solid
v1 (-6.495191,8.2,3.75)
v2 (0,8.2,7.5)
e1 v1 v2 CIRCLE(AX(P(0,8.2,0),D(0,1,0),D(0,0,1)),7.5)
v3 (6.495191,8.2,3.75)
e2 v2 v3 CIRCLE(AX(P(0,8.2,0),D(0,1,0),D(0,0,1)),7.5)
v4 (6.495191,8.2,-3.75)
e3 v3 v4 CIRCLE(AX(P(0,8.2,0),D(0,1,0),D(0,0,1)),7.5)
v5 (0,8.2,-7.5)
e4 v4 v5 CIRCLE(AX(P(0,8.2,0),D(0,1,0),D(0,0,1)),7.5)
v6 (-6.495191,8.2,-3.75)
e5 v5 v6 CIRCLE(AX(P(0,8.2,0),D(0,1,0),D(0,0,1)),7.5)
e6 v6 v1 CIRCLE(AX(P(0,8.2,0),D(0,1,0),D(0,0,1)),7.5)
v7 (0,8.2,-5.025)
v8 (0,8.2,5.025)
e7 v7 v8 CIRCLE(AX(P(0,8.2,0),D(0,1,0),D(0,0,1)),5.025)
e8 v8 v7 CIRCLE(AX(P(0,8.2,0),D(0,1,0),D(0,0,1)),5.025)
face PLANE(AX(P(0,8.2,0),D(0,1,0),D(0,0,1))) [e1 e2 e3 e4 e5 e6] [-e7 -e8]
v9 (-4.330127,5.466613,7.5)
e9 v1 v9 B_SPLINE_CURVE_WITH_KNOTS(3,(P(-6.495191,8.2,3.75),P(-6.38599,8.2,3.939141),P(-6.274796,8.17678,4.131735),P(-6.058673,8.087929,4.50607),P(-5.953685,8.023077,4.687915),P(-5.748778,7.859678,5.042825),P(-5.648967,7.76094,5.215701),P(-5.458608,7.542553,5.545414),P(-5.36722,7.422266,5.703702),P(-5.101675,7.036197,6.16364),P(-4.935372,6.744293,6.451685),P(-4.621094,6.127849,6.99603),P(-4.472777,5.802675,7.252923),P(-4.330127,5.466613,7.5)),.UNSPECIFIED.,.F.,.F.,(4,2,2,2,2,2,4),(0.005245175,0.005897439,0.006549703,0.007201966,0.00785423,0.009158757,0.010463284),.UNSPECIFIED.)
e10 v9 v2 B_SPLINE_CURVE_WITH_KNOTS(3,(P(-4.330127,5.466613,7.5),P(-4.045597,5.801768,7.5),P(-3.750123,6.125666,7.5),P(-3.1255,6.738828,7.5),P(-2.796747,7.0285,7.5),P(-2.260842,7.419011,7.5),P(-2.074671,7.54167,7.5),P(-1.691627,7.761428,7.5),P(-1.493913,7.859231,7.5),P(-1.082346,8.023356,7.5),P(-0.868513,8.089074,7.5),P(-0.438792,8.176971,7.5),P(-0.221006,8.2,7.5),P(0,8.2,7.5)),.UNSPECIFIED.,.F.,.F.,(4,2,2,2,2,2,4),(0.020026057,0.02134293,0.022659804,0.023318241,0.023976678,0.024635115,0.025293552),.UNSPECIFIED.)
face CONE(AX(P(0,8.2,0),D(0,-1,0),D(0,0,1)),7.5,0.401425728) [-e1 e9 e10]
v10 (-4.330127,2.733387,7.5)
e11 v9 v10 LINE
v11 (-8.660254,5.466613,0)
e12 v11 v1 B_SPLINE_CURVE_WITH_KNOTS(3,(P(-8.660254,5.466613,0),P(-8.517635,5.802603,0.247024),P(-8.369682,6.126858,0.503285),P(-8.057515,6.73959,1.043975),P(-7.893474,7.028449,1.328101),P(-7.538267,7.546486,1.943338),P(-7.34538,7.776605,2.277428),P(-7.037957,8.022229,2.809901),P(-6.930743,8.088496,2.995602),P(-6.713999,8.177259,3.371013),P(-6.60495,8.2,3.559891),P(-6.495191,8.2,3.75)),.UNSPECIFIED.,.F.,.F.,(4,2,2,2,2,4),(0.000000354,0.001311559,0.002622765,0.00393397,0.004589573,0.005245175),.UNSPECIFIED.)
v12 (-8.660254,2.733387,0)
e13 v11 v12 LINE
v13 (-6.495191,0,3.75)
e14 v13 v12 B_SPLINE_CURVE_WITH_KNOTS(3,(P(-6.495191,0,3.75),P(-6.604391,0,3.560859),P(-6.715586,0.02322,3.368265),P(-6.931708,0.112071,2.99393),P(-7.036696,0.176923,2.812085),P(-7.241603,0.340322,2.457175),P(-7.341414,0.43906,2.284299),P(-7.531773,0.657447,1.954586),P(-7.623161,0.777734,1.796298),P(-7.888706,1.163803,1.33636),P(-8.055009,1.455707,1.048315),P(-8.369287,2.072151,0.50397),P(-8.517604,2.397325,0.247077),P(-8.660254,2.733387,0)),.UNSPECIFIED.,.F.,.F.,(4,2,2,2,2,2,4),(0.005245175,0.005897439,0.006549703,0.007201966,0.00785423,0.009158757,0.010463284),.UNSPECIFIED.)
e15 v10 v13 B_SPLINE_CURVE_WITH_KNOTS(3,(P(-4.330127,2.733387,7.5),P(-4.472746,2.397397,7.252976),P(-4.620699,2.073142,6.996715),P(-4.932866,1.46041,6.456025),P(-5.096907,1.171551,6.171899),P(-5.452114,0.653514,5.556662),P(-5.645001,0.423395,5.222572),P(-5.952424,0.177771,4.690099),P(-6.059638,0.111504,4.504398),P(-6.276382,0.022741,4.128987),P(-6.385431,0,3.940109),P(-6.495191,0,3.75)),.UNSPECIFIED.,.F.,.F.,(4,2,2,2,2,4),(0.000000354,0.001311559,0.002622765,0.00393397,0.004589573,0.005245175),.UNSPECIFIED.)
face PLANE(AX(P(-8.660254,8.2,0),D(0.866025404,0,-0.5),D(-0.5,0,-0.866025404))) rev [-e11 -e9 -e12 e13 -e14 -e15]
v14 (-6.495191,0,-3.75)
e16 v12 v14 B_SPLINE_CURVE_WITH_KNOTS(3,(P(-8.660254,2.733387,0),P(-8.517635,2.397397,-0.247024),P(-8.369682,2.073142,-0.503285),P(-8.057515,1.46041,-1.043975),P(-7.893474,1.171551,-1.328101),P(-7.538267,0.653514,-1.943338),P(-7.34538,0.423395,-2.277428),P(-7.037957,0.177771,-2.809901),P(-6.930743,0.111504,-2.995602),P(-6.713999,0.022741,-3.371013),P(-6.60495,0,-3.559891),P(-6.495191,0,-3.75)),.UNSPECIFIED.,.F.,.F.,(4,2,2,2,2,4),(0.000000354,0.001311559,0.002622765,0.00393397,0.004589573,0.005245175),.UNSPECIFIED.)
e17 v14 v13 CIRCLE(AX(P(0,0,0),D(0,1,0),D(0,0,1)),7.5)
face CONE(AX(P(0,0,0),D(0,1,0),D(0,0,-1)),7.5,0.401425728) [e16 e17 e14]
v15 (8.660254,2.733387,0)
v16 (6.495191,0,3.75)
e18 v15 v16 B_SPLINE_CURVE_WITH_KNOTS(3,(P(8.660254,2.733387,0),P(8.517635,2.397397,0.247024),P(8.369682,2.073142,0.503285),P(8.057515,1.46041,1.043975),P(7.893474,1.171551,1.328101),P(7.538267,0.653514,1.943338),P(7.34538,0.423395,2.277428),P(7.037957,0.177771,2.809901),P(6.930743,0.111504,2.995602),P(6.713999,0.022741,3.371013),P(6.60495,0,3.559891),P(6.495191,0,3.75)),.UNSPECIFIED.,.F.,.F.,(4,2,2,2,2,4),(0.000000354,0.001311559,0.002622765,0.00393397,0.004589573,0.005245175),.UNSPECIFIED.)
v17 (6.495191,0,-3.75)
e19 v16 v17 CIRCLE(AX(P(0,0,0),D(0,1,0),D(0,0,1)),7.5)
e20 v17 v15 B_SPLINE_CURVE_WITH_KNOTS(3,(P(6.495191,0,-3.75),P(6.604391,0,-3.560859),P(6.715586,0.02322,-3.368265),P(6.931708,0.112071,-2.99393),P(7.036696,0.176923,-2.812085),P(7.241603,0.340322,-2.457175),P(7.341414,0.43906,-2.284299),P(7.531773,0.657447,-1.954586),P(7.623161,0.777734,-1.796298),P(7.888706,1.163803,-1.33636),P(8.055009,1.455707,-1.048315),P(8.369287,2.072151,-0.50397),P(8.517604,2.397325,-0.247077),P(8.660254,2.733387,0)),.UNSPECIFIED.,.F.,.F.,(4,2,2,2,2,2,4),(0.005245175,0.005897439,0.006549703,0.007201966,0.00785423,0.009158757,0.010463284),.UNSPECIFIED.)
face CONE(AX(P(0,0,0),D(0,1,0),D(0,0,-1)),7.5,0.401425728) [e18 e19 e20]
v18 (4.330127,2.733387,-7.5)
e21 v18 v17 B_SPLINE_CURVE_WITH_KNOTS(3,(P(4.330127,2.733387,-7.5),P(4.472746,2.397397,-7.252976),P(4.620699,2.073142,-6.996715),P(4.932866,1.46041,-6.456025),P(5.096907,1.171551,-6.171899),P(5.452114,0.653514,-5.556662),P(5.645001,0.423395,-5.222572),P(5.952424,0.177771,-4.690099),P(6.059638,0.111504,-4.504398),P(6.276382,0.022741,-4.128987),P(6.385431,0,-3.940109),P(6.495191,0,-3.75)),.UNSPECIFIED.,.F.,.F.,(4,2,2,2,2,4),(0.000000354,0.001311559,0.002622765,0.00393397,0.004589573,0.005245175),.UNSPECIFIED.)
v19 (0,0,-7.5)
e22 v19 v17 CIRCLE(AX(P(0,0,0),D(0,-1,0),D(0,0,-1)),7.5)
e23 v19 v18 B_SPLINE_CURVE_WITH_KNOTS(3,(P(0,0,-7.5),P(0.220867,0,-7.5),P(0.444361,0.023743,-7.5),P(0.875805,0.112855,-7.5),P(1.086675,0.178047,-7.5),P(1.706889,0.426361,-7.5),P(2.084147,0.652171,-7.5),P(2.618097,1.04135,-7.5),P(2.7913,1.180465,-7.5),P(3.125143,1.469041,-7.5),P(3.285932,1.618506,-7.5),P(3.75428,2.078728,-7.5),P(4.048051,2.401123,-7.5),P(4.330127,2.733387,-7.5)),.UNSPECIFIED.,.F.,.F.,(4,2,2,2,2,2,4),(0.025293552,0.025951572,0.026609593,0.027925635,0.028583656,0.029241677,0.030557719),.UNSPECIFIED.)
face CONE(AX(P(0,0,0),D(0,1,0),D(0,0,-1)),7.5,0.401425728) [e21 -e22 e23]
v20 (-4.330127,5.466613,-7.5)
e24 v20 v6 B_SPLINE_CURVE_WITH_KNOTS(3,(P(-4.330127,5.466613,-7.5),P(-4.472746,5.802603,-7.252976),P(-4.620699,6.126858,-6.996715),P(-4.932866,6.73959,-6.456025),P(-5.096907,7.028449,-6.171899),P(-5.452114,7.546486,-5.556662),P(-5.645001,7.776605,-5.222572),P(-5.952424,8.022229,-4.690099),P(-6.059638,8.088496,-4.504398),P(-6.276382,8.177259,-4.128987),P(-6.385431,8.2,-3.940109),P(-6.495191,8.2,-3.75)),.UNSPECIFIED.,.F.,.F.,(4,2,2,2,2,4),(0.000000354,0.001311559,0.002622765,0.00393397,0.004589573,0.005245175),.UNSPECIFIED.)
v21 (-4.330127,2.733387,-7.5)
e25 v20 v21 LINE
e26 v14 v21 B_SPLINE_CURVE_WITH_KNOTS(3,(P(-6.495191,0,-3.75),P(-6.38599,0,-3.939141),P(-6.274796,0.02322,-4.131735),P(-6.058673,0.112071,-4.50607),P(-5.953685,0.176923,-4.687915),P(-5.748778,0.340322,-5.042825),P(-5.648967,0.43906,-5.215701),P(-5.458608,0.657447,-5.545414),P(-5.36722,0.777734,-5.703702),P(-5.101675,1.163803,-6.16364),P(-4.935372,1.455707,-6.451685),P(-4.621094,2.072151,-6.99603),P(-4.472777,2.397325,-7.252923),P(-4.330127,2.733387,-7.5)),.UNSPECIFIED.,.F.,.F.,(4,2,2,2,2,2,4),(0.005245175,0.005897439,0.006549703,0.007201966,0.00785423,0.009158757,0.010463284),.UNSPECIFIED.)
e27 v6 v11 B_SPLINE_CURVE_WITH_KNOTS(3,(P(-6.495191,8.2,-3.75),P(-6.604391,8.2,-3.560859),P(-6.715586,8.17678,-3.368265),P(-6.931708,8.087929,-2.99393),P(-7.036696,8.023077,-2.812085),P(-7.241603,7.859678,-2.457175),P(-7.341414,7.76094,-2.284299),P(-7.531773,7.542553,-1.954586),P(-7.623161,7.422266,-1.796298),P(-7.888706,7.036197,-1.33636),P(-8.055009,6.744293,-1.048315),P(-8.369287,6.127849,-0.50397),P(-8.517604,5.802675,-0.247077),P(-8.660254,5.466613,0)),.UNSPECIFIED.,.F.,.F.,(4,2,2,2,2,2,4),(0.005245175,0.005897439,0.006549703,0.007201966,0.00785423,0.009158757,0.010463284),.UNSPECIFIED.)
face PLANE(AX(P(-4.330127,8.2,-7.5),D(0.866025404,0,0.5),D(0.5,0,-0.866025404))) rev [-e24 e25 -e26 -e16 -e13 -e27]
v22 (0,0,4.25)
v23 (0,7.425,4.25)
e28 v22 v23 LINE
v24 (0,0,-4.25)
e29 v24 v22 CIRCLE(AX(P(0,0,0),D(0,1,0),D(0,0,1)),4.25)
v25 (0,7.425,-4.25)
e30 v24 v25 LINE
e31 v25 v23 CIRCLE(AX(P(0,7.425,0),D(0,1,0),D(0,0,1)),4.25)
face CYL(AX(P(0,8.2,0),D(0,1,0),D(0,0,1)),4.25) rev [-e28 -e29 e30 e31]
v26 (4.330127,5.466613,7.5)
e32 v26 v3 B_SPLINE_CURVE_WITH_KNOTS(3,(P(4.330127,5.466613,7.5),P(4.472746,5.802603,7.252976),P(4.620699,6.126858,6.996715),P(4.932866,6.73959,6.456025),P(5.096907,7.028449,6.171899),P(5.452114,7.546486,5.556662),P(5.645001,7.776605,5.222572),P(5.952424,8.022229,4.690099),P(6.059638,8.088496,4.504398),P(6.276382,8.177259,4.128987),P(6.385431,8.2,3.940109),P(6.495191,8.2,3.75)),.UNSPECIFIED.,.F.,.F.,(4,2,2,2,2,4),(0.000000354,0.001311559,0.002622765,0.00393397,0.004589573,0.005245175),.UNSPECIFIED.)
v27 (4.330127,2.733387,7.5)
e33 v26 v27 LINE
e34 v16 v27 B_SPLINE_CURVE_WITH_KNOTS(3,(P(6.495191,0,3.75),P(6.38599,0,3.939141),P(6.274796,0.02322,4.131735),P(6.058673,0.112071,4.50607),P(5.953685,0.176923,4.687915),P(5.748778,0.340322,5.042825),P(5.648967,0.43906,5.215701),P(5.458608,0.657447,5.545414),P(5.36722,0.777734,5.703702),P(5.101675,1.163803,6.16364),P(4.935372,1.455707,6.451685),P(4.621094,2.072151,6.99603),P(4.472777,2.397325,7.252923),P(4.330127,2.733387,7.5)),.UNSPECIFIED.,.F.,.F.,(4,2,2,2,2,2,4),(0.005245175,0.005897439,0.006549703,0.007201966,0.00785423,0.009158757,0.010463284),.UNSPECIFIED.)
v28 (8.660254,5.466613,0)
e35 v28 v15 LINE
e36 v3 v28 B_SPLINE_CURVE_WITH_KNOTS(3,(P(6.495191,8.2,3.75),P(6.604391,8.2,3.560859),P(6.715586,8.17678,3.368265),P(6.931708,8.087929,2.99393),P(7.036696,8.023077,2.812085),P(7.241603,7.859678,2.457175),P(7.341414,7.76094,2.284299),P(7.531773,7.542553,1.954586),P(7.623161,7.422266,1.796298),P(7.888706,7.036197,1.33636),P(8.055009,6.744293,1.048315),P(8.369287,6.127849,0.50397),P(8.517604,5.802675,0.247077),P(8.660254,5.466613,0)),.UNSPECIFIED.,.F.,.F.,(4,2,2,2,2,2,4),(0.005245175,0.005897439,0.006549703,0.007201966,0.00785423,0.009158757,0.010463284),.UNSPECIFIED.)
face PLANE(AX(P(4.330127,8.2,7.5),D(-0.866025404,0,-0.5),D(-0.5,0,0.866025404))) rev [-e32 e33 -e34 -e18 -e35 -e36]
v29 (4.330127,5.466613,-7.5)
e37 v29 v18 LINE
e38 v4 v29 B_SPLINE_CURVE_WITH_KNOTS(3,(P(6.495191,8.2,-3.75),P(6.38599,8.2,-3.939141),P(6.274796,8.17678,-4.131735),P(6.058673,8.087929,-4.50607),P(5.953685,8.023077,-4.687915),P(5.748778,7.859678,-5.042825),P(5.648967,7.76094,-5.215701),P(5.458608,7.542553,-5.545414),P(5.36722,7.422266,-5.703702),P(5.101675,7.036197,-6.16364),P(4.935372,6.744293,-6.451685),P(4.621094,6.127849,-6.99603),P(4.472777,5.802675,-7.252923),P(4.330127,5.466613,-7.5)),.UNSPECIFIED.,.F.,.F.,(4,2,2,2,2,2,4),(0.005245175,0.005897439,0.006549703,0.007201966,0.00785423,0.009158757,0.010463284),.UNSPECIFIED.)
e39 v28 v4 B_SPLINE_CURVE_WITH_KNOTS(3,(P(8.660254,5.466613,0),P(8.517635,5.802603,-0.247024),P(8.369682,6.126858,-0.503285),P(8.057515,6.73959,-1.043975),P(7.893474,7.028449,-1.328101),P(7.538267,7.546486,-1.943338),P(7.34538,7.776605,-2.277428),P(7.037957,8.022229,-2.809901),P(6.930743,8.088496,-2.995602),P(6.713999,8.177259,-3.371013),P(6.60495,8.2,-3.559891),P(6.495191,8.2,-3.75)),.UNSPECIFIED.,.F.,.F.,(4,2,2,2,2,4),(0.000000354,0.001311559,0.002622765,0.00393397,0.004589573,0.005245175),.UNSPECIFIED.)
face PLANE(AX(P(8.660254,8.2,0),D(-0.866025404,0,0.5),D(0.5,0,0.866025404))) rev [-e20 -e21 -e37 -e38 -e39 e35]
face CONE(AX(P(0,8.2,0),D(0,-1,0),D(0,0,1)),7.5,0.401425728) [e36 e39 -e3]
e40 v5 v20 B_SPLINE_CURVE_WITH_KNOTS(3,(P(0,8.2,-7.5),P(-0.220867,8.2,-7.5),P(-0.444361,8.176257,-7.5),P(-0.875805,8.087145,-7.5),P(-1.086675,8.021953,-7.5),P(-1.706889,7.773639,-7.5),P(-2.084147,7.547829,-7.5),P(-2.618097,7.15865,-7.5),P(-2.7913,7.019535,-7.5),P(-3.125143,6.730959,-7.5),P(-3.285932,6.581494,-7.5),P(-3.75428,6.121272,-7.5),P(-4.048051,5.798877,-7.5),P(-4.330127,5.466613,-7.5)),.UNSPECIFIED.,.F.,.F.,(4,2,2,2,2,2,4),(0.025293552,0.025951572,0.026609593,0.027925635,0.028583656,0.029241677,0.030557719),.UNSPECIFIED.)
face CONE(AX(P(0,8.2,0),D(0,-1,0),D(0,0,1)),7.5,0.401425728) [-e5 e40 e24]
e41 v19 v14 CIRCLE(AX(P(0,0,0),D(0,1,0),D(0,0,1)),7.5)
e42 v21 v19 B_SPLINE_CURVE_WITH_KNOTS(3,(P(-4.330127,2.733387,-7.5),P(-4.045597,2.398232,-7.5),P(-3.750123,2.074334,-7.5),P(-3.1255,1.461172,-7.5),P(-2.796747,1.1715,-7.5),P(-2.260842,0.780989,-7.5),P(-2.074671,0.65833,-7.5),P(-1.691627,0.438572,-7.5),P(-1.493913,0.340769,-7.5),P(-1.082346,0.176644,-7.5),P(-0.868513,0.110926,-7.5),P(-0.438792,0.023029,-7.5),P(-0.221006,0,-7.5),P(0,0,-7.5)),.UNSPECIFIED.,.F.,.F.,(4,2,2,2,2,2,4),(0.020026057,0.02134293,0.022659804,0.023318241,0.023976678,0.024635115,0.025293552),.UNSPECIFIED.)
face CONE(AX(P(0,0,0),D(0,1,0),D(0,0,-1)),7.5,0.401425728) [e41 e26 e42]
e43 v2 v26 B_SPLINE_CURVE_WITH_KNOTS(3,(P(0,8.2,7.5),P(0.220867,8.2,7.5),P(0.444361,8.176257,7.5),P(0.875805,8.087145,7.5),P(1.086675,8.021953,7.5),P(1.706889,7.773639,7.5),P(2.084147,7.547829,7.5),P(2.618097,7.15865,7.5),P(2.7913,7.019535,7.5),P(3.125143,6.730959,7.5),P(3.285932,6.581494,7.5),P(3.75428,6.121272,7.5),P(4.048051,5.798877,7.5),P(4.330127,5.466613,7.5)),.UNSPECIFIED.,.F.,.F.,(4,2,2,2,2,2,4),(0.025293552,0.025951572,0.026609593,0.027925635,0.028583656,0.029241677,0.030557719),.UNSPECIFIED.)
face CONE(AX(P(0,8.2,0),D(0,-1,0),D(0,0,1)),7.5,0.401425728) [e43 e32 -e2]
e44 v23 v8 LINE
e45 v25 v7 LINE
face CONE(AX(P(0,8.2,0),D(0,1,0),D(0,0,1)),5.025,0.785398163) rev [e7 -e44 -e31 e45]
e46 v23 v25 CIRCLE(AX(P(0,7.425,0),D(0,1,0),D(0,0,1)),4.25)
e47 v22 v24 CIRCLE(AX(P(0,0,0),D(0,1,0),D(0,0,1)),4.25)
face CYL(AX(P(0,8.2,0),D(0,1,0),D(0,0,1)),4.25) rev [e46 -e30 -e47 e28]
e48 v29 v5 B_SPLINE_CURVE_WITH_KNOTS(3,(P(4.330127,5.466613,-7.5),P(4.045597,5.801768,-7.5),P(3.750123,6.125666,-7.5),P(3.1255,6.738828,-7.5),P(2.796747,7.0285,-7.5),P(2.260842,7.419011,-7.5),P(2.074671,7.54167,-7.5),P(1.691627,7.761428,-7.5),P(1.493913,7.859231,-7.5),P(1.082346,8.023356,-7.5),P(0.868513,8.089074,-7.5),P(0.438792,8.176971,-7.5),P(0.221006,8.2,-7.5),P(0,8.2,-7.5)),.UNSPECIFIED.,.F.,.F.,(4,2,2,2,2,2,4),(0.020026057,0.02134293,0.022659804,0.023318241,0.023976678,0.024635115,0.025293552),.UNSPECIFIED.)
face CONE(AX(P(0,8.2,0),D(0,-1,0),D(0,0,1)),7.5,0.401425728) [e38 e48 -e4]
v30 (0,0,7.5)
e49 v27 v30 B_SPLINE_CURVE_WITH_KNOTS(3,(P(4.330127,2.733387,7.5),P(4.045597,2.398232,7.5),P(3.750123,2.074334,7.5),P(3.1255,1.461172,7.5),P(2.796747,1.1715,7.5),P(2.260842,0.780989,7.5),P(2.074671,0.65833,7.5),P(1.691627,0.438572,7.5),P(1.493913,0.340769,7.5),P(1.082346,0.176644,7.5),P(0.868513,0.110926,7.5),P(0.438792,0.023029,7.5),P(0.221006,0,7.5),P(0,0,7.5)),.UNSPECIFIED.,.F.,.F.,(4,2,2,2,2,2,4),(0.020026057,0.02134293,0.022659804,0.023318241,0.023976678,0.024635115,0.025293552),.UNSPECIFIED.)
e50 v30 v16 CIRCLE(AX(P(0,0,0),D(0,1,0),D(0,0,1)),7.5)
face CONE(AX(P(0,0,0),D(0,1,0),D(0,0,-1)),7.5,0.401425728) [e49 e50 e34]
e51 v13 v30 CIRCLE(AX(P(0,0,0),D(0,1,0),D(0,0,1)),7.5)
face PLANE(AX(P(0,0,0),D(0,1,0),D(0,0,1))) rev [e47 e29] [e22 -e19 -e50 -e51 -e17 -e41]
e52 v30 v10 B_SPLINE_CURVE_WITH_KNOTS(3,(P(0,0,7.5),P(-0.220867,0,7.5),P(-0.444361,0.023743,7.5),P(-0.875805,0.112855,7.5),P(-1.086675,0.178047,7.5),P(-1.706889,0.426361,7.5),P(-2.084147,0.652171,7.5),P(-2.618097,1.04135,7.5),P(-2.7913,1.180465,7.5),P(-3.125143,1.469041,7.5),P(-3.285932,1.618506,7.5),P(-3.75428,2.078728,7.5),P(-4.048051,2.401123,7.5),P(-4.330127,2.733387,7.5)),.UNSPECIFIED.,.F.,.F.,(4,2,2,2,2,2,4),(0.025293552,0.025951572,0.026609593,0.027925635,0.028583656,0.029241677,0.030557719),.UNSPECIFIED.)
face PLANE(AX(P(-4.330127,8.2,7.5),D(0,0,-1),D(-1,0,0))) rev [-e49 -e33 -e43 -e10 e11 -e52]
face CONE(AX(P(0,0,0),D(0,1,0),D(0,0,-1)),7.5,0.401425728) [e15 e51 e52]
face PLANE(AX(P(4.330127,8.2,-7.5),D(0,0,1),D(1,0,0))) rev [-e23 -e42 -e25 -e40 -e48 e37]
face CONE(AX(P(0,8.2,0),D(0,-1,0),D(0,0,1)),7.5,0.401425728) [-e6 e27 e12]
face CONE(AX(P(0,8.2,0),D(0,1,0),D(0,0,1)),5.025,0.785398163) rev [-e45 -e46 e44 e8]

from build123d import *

# Parameters (mm, degrees)
BOSS_EXTRUDE1_DEPTH          = 8.2
SKETCH2_OUTSIDE_W            = 31.148
SKETCH2_OUTSIDE_H            = 28.828
SKETCH2_OUTSIDE_R            = 7.5
CUT_EXTRUDE1_DEPTH           = 8.2
CUT_EXTRUDE1_DRAFT           = -23
SKETCH3_OUTSIDE_W            = 31.148
SKETCH3_OUTSIDE_H            = 28.828
SKETCH3_OUTSIDE_R            = 7.5
CUT_EXTRUDE2_DEPTH           = 8.2
CUT_EXTRUDE2_DRAFT           = -23
M10_TAPPED_HOLE1_D           = 8.5
M10_TAPPED_HOLE1_CSINK_D     = 10.05
M10_TAPPED_HOLE1_CSINK_ANGLE = 90


with BuildPart() as part:
    # Sketch1 → Boss-Extrude1 (new body)
    with BuildSketch(Plane(origin=(0, 0, 0), x_dir=(1, 0, 0), z_dir=(0, 1, 0))):
        Polygon((4.330127019, 7.5), (-4.330127019, 7.5), (-8.660254038, 0), (-4.330127019, -7.5), (4.330127019, -7.5), (8.660254038, 0), align=None)
    extrude(amount=BOSS_EXTRUDE1_DEPTH)


with BuildPart() as cut_extrude1_tool:
    # Sketch2 outside → Cut-Extrude1 (with draft: the straight prism first)
    with BuildSketch(Plane(origin=(0, 8.2, 0), x_dir=(1, 0, 0), z_dir=(0, 1, 0))):
        Rectangle(SKETCH2_OUTSIDE_W, SKETCH2_OUTSIDE_H)
        Circle(SKETCH2_OUTSIDE_R, mode=Mode.SUBTRACT)
    extrude(amount=-CUT_EXTRUDE1_DEPTH)
    # Cut-Extrude1: the draft: its side faces are tilted about the plane it starts from
    cut_extrude1_sides = [cut_extrude1_tool.faces().sort_by_distance(p)[0] for p in [
        (0, 4.1, 14.414),
        (15.574, 4.1, 0),
        (0, 4.1, -14.414),
        (-15.574, 4.1, 0),
        (-7.5, 4.1, 0),
    ]]
    draft(cut_extrude1_sides, Plane(origin=(0, 8.2, 0), x_dir=(1, 0, 0), z_dir=(0, 1, 0)), CUT_EXTRUDE1_DRAFT)


with BuildPart() as part_1:
    add(part.part)

    # Cut-Extrude1: cut by cut_extrude1_tool
    add(cut_extrude1_tool.part, mode=Mode.SUBTRACT)


with BuildPart() as cut_extrude2_tool:
    # Sketch3 outside → Cut-Extrude2 (with draft: the straight prism first)
    with BuildSketch(Plane.XZ):
        Rectangle(SKETCH3_OUTSIDE_W, SKETCH3_OUTSIDE_H)
        Circle(SKETCH3_OUTSIDE_R, mode=Mode.SUBTRACT)
    extrude(amount=-CUT_EXTRUDE2_DEPTH)
    # Cut-Extrude2: the draft: its side faces are tilted about the plane it starts from
    cut_extrude2_sides = [cut_extrude2_tool.faces().sort_by_distance(p)[0] for p in [
        (0, 4.1, -14.414),
        (15.574, 4.1, 0),
        (0, 4.1, 14.414),
        (-15.574, 4.1, 0),
        (-7.5, 4.1, 0),
    ]]
    draft(cut_extrude2_sides, Plane.XZ, CUT_EXTRUDE2_DRAFT)


with BuildPart() as part_2:
    add(part_1.part)

    # Cut-Extrude2: cut by cut_extrude2_tool
    add(cut_extrude2_tool.part, mode=Mode.SUBTRACT)

    # M10 Tapped Hole1 (through all)
    with Locations(Plane(origin=(0, 8.2, 0), x_dir=(1, 0, 0), z_dir=(0, 1, 0))):
        with Locations((0, 0)):
            CounterSinkHole(M10_TAPPED_HOLE1_D / 2, M10_TAPPED_HOLE1_CSINK_D / 2, counter_sink_angle=M10_TAPPED_HOLE1_CSINK_ANGLE)


solid = part_2.part
